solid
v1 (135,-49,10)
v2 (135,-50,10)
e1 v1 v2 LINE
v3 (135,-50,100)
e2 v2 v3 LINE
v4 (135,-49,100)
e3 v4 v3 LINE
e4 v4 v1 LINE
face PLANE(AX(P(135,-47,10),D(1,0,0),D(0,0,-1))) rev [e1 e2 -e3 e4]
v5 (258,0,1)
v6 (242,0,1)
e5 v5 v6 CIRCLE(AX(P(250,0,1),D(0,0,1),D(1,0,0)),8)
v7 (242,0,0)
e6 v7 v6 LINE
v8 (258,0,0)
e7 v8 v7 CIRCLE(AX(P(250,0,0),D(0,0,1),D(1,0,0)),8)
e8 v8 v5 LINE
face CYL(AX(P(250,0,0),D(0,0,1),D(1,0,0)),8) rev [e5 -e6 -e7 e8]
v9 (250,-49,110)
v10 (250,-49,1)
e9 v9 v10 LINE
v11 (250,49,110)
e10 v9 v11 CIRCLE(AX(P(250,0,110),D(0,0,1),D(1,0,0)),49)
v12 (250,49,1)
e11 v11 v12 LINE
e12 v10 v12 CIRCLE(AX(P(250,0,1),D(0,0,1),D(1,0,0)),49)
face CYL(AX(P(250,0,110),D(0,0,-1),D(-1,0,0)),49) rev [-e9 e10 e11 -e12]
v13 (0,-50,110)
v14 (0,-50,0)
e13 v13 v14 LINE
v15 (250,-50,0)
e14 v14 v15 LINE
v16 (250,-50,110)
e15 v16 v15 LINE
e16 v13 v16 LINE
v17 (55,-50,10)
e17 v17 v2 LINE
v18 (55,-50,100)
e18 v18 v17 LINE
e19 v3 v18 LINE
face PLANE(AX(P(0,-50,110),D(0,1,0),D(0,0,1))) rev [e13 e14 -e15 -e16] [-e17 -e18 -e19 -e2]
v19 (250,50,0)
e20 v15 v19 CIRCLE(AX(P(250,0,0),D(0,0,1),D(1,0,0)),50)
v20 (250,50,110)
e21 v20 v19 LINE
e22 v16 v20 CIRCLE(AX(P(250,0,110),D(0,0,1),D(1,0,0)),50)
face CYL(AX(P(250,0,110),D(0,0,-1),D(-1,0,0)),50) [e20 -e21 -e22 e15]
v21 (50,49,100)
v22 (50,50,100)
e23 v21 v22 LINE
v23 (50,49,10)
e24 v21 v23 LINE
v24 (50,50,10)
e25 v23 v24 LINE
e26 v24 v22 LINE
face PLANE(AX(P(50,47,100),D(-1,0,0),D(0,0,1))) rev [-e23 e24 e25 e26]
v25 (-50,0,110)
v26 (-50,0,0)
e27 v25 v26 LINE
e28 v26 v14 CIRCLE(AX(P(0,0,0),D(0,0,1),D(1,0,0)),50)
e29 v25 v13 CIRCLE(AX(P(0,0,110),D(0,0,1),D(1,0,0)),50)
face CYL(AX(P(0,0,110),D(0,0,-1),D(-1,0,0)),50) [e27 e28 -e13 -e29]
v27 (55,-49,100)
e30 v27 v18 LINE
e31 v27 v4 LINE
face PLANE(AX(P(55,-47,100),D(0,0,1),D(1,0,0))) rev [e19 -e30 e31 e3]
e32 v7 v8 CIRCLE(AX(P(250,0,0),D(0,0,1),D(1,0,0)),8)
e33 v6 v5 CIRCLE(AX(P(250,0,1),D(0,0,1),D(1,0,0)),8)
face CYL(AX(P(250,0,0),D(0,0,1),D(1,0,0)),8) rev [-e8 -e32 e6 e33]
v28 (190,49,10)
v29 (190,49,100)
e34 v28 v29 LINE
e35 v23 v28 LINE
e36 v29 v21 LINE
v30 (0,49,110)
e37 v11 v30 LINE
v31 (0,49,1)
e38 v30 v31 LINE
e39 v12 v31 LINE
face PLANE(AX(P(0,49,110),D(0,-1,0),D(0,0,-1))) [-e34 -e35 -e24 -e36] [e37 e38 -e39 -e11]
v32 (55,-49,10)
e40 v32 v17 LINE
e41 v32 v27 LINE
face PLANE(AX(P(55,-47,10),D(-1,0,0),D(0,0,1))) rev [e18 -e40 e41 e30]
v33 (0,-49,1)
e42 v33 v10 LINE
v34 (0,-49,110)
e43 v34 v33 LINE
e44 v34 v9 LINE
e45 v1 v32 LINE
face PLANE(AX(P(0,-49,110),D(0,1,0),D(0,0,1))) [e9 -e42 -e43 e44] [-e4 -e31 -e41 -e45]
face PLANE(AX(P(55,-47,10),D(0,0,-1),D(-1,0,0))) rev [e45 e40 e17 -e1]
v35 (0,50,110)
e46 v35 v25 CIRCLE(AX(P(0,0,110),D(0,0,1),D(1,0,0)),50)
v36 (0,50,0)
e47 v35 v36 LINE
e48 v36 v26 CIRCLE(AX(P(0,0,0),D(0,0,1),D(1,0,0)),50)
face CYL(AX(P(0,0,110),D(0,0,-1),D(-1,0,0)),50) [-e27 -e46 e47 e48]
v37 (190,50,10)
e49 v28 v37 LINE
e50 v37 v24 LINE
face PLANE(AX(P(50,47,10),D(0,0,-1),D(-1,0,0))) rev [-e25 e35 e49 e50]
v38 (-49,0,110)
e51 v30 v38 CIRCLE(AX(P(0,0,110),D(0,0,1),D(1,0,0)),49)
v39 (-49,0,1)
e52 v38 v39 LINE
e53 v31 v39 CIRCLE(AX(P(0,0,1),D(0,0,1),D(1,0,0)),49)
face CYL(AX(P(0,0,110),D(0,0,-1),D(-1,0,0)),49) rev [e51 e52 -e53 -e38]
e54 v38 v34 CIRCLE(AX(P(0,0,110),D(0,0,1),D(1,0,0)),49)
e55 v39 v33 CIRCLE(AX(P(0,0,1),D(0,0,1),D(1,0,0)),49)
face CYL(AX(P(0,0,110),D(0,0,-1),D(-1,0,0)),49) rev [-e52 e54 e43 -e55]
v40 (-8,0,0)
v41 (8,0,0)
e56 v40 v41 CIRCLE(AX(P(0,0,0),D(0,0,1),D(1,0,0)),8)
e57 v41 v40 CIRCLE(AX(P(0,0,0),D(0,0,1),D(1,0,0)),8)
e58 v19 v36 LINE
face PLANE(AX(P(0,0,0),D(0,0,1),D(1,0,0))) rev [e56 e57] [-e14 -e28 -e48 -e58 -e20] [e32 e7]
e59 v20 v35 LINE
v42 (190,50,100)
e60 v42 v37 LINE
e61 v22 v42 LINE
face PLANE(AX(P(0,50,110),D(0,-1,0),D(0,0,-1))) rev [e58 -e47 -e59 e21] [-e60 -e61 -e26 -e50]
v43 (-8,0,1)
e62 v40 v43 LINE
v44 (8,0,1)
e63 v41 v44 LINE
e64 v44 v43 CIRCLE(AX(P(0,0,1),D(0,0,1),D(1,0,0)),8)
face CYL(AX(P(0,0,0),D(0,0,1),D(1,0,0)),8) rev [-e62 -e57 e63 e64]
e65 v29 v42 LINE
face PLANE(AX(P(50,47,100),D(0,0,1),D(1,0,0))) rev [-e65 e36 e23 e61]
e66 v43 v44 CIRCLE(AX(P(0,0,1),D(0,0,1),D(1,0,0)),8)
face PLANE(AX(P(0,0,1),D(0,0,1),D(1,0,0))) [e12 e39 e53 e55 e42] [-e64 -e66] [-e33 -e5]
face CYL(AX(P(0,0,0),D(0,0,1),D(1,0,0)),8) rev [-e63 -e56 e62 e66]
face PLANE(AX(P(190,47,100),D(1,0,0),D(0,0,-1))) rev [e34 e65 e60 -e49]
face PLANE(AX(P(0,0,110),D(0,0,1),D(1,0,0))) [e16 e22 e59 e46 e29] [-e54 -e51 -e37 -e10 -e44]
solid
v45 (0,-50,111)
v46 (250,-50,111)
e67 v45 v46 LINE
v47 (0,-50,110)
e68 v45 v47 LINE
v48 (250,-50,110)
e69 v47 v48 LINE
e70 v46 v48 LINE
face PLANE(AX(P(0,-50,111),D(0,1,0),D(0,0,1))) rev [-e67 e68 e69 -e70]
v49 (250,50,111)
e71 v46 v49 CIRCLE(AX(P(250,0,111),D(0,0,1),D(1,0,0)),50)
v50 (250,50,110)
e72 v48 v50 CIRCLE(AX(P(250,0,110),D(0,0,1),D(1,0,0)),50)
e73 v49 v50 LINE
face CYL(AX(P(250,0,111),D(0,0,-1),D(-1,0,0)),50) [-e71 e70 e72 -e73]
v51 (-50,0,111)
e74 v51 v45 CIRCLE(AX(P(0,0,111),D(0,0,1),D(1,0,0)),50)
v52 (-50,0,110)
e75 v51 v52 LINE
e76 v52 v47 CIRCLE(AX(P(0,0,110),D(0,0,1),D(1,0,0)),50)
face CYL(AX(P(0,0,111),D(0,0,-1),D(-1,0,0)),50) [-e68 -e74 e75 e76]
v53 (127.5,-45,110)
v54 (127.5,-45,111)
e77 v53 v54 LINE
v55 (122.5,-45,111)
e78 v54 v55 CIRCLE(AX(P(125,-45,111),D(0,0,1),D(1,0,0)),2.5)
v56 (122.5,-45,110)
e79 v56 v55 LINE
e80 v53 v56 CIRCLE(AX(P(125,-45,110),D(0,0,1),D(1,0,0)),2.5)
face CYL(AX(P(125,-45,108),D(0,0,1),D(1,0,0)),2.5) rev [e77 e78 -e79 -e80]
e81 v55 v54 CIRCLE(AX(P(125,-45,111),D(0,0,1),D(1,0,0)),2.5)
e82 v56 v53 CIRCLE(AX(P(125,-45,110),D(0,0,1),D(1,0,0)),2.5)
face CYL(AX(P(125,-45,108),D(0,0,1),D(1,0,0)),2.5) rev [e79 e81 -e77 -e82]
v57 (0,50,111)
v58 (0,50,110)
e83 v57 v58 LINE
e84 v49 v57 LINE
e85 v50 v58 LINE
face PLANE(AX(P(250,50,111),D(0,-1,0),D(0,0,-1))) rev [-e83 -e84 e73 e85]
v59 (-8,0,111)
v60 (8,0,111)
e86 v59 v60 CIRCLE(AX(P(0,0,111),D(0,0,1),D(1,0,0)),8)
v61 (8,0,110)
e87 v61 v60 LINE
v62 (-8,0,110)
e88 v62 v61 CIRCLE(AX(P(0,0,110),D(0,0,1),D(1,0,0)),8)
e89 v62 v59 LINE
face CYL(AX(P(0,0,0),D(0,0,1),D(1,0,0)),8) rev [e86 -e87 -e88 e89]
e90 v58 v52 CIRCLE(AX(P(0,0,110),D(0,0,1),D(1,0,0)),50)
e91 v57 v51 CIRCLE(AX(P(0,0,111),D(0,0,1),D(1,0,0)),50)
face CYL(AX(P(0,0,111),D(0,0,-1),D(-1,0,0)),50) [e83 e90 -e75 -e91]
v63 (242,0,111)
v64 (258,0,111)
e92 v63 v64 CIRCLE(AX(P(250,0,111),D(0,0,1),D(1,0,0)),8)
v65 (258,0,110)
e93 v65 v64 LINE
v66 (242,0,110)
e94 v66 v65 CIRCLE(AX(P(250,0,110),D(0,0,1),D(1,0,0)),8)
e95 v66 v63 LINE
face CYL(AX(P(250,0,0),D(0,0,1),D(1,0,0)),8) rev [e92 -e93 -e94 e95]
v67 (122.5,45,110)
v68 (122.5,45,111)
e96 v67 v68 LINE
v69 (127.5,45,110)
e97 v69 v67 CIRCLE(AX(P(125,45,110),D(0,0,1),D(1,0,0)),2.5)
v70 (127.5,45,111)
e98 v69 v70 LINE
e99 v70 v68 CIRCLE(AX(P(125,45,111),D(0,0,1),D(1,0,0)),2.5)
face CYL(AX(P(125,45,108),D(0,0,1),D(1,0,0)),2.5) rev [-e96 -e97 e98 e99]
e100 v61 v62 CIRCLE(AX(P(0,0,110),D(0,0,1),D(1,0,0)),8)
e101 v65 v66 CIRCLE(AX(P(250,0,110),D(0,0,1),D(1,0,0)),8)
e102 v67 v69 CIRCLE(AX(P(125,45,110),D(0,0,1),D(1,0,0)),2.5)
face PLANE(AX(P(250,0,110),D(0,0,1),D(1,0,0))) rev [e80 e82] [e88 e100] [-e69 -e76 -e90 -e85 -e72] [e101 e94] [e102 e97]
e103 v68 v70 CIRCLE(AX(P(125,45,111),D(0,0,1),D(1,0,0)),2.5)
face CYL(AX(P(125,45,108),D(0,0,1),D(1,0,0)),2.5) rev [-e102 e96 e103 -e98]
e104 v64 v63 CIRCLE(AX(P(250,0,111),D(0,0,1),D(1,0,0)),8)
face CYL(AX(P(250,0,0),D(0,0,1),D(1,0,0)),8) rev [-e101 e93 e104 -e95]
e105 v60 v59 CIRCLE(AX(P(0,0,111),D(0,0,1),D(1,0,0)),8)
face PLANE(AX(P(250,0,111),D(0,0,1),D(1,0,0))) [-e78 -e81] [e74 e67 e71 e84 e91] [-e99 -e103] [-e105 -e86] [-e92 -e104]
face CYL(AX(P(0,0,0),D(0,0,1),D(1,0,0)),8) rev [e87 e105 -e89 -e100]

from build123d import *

# Parameters (mm, degrees)
EXTRUDE_1_DEPTH     = 110
SHELL_1_T           = -1
EXTRUDE_2_DEPTH     = 1
SKETCH_3_R          = 8
CUT_EXTRUDE_1_DEPTH = 324.760714108
SKETCH_5_R          = 2.5
CUT_EXTRUDE_2_DEPTH = 3
SKETCH_6_W          = 80
SKETCH_6_H          = 90
CUT_EXTRUDE_3_DEPTH = 3
SKETCH_7_W          = 140
SKETCH_7_H          = 90
CUT_EXTRUDE_4_DEPTH = 3


with BuildPart() as part:
    # 草图1 → 凸台-拉伸1 (new body)
    with BuildSketch(Plane.XY):
        with BuildLine():
            Line((0, 50), (250, 50))
            ThreePointArc((250, 50), (300, 0), (250, -50))
            Line((250, -50), (0, -50))
            ThreePointArc((0, -50), (-50, 0), (0, 50))
        make_face()
    extrude(amount=EXTRUDE_1_DEPTH)

    # 抽壳1
    shell_1_openings = [part.faces().sort_by_distance(p)[0] for p in [
        (125, 0, 110),
    ]]
    offset(amount=SHELL_1_T, openings=shell_1_openings, kind=Kind.INTERSECTION)


with BuildPart() as body_2:
    # 草图2 → 凸台-拉伸2 (new body)
    with BuildSketch(Plane.XY.offset(110)):
        with BuildLine():
            Line((0, -50), (250, -50))
            ThreePointArc((250, -50), (300, 0), (250, 50))
            Line((250, 50), (0, 50))
            ThreePointArc((0, 50), (-50, 0), (0, -50))
        make_face()
    extrude(amount=EXTRUDE_2_DEPTH)


with BuildPart() as cut_extrude_1_tool:
    # 草图3 → 切除-拉伸1 (new, through all)
    with BuildSketch(Plane.XY.offset(111)):
        Circle(SKETCH_3_R)
        with Locations((250, 0)):
            Circle(SKETCH_3_R)
    extrude(amount=-CUT_EXTRUDE_1_DEPTH)


with BuildPart() as part_1:
    add(part.part)

    # 切除-拉伸1: cut by cut_extrude_1_tool
    add(cut_extrude_1_tool.part, mode=Mode.SUBTRACT)

    # 草图6 → 切除-拉伸3 (cut)
    with BuildSketch(Plane.XZ.offset(50)):
        with Locations((95, 55)):
            Rectangle(SKETCH_6_W, SKETCH_6_H)
    extrude(amount=-CUT_EXTRUDE_3_DEPTH, mode=Mode.SUBTRACT)

    # 草图7 → 切除-拉伸4 (cut)
    with BuildSketch(Plane(origin=(0, 50, 0), x_dir=(1, 0, 0), z_dir=(0, 1, 0))):
        with Locations((120, -55)):
            Rectangle(SKETCH_7_W, SKETCH_7_H)
    extrude(amount=-CUT_EXTRUDE_4_DEPTH, mode=Mode.SUBTRACT)


with BuildPart() as body_2_1:
    add(body_2.part)

    # 切除-拉伸1: cut by cut_extrude_1_tool
    add(cut_extrude_1_tool.part, mode=Mode.SUBTRACT)

    # 草图5 → 切除-拉伸2 (cut)
    with BuildSketch(Plane.XY.offset(111)):
        with Locations((-100, 45)):
            Circle(SKETCH_5_R)
        with Locations((350, 45)):
            Circle(SKETCH_5_R)
        with Locations((-100, -45)):
            Circle(SKETCH_5_R)
        with Locations((350, -45)):
            Circle(SKETCH_5_R)
        with Locations((420, 0)):
            Circle(SKETCH_5_R)
        with Locations((-170, 0)):
            Circle(SKETCH_5_R)
        with Locations((125, 45)):
            Circle(SKETCH_5_R)
        with Locations((125, -45)):
            Circle(SKETCH_5_R)
    extrude(amount=-CUT_EXTRUDE_2_DEPTH, mode=Mode.SUBTRACT)


solid = Compound([part_1.part, body_2_1.part])
